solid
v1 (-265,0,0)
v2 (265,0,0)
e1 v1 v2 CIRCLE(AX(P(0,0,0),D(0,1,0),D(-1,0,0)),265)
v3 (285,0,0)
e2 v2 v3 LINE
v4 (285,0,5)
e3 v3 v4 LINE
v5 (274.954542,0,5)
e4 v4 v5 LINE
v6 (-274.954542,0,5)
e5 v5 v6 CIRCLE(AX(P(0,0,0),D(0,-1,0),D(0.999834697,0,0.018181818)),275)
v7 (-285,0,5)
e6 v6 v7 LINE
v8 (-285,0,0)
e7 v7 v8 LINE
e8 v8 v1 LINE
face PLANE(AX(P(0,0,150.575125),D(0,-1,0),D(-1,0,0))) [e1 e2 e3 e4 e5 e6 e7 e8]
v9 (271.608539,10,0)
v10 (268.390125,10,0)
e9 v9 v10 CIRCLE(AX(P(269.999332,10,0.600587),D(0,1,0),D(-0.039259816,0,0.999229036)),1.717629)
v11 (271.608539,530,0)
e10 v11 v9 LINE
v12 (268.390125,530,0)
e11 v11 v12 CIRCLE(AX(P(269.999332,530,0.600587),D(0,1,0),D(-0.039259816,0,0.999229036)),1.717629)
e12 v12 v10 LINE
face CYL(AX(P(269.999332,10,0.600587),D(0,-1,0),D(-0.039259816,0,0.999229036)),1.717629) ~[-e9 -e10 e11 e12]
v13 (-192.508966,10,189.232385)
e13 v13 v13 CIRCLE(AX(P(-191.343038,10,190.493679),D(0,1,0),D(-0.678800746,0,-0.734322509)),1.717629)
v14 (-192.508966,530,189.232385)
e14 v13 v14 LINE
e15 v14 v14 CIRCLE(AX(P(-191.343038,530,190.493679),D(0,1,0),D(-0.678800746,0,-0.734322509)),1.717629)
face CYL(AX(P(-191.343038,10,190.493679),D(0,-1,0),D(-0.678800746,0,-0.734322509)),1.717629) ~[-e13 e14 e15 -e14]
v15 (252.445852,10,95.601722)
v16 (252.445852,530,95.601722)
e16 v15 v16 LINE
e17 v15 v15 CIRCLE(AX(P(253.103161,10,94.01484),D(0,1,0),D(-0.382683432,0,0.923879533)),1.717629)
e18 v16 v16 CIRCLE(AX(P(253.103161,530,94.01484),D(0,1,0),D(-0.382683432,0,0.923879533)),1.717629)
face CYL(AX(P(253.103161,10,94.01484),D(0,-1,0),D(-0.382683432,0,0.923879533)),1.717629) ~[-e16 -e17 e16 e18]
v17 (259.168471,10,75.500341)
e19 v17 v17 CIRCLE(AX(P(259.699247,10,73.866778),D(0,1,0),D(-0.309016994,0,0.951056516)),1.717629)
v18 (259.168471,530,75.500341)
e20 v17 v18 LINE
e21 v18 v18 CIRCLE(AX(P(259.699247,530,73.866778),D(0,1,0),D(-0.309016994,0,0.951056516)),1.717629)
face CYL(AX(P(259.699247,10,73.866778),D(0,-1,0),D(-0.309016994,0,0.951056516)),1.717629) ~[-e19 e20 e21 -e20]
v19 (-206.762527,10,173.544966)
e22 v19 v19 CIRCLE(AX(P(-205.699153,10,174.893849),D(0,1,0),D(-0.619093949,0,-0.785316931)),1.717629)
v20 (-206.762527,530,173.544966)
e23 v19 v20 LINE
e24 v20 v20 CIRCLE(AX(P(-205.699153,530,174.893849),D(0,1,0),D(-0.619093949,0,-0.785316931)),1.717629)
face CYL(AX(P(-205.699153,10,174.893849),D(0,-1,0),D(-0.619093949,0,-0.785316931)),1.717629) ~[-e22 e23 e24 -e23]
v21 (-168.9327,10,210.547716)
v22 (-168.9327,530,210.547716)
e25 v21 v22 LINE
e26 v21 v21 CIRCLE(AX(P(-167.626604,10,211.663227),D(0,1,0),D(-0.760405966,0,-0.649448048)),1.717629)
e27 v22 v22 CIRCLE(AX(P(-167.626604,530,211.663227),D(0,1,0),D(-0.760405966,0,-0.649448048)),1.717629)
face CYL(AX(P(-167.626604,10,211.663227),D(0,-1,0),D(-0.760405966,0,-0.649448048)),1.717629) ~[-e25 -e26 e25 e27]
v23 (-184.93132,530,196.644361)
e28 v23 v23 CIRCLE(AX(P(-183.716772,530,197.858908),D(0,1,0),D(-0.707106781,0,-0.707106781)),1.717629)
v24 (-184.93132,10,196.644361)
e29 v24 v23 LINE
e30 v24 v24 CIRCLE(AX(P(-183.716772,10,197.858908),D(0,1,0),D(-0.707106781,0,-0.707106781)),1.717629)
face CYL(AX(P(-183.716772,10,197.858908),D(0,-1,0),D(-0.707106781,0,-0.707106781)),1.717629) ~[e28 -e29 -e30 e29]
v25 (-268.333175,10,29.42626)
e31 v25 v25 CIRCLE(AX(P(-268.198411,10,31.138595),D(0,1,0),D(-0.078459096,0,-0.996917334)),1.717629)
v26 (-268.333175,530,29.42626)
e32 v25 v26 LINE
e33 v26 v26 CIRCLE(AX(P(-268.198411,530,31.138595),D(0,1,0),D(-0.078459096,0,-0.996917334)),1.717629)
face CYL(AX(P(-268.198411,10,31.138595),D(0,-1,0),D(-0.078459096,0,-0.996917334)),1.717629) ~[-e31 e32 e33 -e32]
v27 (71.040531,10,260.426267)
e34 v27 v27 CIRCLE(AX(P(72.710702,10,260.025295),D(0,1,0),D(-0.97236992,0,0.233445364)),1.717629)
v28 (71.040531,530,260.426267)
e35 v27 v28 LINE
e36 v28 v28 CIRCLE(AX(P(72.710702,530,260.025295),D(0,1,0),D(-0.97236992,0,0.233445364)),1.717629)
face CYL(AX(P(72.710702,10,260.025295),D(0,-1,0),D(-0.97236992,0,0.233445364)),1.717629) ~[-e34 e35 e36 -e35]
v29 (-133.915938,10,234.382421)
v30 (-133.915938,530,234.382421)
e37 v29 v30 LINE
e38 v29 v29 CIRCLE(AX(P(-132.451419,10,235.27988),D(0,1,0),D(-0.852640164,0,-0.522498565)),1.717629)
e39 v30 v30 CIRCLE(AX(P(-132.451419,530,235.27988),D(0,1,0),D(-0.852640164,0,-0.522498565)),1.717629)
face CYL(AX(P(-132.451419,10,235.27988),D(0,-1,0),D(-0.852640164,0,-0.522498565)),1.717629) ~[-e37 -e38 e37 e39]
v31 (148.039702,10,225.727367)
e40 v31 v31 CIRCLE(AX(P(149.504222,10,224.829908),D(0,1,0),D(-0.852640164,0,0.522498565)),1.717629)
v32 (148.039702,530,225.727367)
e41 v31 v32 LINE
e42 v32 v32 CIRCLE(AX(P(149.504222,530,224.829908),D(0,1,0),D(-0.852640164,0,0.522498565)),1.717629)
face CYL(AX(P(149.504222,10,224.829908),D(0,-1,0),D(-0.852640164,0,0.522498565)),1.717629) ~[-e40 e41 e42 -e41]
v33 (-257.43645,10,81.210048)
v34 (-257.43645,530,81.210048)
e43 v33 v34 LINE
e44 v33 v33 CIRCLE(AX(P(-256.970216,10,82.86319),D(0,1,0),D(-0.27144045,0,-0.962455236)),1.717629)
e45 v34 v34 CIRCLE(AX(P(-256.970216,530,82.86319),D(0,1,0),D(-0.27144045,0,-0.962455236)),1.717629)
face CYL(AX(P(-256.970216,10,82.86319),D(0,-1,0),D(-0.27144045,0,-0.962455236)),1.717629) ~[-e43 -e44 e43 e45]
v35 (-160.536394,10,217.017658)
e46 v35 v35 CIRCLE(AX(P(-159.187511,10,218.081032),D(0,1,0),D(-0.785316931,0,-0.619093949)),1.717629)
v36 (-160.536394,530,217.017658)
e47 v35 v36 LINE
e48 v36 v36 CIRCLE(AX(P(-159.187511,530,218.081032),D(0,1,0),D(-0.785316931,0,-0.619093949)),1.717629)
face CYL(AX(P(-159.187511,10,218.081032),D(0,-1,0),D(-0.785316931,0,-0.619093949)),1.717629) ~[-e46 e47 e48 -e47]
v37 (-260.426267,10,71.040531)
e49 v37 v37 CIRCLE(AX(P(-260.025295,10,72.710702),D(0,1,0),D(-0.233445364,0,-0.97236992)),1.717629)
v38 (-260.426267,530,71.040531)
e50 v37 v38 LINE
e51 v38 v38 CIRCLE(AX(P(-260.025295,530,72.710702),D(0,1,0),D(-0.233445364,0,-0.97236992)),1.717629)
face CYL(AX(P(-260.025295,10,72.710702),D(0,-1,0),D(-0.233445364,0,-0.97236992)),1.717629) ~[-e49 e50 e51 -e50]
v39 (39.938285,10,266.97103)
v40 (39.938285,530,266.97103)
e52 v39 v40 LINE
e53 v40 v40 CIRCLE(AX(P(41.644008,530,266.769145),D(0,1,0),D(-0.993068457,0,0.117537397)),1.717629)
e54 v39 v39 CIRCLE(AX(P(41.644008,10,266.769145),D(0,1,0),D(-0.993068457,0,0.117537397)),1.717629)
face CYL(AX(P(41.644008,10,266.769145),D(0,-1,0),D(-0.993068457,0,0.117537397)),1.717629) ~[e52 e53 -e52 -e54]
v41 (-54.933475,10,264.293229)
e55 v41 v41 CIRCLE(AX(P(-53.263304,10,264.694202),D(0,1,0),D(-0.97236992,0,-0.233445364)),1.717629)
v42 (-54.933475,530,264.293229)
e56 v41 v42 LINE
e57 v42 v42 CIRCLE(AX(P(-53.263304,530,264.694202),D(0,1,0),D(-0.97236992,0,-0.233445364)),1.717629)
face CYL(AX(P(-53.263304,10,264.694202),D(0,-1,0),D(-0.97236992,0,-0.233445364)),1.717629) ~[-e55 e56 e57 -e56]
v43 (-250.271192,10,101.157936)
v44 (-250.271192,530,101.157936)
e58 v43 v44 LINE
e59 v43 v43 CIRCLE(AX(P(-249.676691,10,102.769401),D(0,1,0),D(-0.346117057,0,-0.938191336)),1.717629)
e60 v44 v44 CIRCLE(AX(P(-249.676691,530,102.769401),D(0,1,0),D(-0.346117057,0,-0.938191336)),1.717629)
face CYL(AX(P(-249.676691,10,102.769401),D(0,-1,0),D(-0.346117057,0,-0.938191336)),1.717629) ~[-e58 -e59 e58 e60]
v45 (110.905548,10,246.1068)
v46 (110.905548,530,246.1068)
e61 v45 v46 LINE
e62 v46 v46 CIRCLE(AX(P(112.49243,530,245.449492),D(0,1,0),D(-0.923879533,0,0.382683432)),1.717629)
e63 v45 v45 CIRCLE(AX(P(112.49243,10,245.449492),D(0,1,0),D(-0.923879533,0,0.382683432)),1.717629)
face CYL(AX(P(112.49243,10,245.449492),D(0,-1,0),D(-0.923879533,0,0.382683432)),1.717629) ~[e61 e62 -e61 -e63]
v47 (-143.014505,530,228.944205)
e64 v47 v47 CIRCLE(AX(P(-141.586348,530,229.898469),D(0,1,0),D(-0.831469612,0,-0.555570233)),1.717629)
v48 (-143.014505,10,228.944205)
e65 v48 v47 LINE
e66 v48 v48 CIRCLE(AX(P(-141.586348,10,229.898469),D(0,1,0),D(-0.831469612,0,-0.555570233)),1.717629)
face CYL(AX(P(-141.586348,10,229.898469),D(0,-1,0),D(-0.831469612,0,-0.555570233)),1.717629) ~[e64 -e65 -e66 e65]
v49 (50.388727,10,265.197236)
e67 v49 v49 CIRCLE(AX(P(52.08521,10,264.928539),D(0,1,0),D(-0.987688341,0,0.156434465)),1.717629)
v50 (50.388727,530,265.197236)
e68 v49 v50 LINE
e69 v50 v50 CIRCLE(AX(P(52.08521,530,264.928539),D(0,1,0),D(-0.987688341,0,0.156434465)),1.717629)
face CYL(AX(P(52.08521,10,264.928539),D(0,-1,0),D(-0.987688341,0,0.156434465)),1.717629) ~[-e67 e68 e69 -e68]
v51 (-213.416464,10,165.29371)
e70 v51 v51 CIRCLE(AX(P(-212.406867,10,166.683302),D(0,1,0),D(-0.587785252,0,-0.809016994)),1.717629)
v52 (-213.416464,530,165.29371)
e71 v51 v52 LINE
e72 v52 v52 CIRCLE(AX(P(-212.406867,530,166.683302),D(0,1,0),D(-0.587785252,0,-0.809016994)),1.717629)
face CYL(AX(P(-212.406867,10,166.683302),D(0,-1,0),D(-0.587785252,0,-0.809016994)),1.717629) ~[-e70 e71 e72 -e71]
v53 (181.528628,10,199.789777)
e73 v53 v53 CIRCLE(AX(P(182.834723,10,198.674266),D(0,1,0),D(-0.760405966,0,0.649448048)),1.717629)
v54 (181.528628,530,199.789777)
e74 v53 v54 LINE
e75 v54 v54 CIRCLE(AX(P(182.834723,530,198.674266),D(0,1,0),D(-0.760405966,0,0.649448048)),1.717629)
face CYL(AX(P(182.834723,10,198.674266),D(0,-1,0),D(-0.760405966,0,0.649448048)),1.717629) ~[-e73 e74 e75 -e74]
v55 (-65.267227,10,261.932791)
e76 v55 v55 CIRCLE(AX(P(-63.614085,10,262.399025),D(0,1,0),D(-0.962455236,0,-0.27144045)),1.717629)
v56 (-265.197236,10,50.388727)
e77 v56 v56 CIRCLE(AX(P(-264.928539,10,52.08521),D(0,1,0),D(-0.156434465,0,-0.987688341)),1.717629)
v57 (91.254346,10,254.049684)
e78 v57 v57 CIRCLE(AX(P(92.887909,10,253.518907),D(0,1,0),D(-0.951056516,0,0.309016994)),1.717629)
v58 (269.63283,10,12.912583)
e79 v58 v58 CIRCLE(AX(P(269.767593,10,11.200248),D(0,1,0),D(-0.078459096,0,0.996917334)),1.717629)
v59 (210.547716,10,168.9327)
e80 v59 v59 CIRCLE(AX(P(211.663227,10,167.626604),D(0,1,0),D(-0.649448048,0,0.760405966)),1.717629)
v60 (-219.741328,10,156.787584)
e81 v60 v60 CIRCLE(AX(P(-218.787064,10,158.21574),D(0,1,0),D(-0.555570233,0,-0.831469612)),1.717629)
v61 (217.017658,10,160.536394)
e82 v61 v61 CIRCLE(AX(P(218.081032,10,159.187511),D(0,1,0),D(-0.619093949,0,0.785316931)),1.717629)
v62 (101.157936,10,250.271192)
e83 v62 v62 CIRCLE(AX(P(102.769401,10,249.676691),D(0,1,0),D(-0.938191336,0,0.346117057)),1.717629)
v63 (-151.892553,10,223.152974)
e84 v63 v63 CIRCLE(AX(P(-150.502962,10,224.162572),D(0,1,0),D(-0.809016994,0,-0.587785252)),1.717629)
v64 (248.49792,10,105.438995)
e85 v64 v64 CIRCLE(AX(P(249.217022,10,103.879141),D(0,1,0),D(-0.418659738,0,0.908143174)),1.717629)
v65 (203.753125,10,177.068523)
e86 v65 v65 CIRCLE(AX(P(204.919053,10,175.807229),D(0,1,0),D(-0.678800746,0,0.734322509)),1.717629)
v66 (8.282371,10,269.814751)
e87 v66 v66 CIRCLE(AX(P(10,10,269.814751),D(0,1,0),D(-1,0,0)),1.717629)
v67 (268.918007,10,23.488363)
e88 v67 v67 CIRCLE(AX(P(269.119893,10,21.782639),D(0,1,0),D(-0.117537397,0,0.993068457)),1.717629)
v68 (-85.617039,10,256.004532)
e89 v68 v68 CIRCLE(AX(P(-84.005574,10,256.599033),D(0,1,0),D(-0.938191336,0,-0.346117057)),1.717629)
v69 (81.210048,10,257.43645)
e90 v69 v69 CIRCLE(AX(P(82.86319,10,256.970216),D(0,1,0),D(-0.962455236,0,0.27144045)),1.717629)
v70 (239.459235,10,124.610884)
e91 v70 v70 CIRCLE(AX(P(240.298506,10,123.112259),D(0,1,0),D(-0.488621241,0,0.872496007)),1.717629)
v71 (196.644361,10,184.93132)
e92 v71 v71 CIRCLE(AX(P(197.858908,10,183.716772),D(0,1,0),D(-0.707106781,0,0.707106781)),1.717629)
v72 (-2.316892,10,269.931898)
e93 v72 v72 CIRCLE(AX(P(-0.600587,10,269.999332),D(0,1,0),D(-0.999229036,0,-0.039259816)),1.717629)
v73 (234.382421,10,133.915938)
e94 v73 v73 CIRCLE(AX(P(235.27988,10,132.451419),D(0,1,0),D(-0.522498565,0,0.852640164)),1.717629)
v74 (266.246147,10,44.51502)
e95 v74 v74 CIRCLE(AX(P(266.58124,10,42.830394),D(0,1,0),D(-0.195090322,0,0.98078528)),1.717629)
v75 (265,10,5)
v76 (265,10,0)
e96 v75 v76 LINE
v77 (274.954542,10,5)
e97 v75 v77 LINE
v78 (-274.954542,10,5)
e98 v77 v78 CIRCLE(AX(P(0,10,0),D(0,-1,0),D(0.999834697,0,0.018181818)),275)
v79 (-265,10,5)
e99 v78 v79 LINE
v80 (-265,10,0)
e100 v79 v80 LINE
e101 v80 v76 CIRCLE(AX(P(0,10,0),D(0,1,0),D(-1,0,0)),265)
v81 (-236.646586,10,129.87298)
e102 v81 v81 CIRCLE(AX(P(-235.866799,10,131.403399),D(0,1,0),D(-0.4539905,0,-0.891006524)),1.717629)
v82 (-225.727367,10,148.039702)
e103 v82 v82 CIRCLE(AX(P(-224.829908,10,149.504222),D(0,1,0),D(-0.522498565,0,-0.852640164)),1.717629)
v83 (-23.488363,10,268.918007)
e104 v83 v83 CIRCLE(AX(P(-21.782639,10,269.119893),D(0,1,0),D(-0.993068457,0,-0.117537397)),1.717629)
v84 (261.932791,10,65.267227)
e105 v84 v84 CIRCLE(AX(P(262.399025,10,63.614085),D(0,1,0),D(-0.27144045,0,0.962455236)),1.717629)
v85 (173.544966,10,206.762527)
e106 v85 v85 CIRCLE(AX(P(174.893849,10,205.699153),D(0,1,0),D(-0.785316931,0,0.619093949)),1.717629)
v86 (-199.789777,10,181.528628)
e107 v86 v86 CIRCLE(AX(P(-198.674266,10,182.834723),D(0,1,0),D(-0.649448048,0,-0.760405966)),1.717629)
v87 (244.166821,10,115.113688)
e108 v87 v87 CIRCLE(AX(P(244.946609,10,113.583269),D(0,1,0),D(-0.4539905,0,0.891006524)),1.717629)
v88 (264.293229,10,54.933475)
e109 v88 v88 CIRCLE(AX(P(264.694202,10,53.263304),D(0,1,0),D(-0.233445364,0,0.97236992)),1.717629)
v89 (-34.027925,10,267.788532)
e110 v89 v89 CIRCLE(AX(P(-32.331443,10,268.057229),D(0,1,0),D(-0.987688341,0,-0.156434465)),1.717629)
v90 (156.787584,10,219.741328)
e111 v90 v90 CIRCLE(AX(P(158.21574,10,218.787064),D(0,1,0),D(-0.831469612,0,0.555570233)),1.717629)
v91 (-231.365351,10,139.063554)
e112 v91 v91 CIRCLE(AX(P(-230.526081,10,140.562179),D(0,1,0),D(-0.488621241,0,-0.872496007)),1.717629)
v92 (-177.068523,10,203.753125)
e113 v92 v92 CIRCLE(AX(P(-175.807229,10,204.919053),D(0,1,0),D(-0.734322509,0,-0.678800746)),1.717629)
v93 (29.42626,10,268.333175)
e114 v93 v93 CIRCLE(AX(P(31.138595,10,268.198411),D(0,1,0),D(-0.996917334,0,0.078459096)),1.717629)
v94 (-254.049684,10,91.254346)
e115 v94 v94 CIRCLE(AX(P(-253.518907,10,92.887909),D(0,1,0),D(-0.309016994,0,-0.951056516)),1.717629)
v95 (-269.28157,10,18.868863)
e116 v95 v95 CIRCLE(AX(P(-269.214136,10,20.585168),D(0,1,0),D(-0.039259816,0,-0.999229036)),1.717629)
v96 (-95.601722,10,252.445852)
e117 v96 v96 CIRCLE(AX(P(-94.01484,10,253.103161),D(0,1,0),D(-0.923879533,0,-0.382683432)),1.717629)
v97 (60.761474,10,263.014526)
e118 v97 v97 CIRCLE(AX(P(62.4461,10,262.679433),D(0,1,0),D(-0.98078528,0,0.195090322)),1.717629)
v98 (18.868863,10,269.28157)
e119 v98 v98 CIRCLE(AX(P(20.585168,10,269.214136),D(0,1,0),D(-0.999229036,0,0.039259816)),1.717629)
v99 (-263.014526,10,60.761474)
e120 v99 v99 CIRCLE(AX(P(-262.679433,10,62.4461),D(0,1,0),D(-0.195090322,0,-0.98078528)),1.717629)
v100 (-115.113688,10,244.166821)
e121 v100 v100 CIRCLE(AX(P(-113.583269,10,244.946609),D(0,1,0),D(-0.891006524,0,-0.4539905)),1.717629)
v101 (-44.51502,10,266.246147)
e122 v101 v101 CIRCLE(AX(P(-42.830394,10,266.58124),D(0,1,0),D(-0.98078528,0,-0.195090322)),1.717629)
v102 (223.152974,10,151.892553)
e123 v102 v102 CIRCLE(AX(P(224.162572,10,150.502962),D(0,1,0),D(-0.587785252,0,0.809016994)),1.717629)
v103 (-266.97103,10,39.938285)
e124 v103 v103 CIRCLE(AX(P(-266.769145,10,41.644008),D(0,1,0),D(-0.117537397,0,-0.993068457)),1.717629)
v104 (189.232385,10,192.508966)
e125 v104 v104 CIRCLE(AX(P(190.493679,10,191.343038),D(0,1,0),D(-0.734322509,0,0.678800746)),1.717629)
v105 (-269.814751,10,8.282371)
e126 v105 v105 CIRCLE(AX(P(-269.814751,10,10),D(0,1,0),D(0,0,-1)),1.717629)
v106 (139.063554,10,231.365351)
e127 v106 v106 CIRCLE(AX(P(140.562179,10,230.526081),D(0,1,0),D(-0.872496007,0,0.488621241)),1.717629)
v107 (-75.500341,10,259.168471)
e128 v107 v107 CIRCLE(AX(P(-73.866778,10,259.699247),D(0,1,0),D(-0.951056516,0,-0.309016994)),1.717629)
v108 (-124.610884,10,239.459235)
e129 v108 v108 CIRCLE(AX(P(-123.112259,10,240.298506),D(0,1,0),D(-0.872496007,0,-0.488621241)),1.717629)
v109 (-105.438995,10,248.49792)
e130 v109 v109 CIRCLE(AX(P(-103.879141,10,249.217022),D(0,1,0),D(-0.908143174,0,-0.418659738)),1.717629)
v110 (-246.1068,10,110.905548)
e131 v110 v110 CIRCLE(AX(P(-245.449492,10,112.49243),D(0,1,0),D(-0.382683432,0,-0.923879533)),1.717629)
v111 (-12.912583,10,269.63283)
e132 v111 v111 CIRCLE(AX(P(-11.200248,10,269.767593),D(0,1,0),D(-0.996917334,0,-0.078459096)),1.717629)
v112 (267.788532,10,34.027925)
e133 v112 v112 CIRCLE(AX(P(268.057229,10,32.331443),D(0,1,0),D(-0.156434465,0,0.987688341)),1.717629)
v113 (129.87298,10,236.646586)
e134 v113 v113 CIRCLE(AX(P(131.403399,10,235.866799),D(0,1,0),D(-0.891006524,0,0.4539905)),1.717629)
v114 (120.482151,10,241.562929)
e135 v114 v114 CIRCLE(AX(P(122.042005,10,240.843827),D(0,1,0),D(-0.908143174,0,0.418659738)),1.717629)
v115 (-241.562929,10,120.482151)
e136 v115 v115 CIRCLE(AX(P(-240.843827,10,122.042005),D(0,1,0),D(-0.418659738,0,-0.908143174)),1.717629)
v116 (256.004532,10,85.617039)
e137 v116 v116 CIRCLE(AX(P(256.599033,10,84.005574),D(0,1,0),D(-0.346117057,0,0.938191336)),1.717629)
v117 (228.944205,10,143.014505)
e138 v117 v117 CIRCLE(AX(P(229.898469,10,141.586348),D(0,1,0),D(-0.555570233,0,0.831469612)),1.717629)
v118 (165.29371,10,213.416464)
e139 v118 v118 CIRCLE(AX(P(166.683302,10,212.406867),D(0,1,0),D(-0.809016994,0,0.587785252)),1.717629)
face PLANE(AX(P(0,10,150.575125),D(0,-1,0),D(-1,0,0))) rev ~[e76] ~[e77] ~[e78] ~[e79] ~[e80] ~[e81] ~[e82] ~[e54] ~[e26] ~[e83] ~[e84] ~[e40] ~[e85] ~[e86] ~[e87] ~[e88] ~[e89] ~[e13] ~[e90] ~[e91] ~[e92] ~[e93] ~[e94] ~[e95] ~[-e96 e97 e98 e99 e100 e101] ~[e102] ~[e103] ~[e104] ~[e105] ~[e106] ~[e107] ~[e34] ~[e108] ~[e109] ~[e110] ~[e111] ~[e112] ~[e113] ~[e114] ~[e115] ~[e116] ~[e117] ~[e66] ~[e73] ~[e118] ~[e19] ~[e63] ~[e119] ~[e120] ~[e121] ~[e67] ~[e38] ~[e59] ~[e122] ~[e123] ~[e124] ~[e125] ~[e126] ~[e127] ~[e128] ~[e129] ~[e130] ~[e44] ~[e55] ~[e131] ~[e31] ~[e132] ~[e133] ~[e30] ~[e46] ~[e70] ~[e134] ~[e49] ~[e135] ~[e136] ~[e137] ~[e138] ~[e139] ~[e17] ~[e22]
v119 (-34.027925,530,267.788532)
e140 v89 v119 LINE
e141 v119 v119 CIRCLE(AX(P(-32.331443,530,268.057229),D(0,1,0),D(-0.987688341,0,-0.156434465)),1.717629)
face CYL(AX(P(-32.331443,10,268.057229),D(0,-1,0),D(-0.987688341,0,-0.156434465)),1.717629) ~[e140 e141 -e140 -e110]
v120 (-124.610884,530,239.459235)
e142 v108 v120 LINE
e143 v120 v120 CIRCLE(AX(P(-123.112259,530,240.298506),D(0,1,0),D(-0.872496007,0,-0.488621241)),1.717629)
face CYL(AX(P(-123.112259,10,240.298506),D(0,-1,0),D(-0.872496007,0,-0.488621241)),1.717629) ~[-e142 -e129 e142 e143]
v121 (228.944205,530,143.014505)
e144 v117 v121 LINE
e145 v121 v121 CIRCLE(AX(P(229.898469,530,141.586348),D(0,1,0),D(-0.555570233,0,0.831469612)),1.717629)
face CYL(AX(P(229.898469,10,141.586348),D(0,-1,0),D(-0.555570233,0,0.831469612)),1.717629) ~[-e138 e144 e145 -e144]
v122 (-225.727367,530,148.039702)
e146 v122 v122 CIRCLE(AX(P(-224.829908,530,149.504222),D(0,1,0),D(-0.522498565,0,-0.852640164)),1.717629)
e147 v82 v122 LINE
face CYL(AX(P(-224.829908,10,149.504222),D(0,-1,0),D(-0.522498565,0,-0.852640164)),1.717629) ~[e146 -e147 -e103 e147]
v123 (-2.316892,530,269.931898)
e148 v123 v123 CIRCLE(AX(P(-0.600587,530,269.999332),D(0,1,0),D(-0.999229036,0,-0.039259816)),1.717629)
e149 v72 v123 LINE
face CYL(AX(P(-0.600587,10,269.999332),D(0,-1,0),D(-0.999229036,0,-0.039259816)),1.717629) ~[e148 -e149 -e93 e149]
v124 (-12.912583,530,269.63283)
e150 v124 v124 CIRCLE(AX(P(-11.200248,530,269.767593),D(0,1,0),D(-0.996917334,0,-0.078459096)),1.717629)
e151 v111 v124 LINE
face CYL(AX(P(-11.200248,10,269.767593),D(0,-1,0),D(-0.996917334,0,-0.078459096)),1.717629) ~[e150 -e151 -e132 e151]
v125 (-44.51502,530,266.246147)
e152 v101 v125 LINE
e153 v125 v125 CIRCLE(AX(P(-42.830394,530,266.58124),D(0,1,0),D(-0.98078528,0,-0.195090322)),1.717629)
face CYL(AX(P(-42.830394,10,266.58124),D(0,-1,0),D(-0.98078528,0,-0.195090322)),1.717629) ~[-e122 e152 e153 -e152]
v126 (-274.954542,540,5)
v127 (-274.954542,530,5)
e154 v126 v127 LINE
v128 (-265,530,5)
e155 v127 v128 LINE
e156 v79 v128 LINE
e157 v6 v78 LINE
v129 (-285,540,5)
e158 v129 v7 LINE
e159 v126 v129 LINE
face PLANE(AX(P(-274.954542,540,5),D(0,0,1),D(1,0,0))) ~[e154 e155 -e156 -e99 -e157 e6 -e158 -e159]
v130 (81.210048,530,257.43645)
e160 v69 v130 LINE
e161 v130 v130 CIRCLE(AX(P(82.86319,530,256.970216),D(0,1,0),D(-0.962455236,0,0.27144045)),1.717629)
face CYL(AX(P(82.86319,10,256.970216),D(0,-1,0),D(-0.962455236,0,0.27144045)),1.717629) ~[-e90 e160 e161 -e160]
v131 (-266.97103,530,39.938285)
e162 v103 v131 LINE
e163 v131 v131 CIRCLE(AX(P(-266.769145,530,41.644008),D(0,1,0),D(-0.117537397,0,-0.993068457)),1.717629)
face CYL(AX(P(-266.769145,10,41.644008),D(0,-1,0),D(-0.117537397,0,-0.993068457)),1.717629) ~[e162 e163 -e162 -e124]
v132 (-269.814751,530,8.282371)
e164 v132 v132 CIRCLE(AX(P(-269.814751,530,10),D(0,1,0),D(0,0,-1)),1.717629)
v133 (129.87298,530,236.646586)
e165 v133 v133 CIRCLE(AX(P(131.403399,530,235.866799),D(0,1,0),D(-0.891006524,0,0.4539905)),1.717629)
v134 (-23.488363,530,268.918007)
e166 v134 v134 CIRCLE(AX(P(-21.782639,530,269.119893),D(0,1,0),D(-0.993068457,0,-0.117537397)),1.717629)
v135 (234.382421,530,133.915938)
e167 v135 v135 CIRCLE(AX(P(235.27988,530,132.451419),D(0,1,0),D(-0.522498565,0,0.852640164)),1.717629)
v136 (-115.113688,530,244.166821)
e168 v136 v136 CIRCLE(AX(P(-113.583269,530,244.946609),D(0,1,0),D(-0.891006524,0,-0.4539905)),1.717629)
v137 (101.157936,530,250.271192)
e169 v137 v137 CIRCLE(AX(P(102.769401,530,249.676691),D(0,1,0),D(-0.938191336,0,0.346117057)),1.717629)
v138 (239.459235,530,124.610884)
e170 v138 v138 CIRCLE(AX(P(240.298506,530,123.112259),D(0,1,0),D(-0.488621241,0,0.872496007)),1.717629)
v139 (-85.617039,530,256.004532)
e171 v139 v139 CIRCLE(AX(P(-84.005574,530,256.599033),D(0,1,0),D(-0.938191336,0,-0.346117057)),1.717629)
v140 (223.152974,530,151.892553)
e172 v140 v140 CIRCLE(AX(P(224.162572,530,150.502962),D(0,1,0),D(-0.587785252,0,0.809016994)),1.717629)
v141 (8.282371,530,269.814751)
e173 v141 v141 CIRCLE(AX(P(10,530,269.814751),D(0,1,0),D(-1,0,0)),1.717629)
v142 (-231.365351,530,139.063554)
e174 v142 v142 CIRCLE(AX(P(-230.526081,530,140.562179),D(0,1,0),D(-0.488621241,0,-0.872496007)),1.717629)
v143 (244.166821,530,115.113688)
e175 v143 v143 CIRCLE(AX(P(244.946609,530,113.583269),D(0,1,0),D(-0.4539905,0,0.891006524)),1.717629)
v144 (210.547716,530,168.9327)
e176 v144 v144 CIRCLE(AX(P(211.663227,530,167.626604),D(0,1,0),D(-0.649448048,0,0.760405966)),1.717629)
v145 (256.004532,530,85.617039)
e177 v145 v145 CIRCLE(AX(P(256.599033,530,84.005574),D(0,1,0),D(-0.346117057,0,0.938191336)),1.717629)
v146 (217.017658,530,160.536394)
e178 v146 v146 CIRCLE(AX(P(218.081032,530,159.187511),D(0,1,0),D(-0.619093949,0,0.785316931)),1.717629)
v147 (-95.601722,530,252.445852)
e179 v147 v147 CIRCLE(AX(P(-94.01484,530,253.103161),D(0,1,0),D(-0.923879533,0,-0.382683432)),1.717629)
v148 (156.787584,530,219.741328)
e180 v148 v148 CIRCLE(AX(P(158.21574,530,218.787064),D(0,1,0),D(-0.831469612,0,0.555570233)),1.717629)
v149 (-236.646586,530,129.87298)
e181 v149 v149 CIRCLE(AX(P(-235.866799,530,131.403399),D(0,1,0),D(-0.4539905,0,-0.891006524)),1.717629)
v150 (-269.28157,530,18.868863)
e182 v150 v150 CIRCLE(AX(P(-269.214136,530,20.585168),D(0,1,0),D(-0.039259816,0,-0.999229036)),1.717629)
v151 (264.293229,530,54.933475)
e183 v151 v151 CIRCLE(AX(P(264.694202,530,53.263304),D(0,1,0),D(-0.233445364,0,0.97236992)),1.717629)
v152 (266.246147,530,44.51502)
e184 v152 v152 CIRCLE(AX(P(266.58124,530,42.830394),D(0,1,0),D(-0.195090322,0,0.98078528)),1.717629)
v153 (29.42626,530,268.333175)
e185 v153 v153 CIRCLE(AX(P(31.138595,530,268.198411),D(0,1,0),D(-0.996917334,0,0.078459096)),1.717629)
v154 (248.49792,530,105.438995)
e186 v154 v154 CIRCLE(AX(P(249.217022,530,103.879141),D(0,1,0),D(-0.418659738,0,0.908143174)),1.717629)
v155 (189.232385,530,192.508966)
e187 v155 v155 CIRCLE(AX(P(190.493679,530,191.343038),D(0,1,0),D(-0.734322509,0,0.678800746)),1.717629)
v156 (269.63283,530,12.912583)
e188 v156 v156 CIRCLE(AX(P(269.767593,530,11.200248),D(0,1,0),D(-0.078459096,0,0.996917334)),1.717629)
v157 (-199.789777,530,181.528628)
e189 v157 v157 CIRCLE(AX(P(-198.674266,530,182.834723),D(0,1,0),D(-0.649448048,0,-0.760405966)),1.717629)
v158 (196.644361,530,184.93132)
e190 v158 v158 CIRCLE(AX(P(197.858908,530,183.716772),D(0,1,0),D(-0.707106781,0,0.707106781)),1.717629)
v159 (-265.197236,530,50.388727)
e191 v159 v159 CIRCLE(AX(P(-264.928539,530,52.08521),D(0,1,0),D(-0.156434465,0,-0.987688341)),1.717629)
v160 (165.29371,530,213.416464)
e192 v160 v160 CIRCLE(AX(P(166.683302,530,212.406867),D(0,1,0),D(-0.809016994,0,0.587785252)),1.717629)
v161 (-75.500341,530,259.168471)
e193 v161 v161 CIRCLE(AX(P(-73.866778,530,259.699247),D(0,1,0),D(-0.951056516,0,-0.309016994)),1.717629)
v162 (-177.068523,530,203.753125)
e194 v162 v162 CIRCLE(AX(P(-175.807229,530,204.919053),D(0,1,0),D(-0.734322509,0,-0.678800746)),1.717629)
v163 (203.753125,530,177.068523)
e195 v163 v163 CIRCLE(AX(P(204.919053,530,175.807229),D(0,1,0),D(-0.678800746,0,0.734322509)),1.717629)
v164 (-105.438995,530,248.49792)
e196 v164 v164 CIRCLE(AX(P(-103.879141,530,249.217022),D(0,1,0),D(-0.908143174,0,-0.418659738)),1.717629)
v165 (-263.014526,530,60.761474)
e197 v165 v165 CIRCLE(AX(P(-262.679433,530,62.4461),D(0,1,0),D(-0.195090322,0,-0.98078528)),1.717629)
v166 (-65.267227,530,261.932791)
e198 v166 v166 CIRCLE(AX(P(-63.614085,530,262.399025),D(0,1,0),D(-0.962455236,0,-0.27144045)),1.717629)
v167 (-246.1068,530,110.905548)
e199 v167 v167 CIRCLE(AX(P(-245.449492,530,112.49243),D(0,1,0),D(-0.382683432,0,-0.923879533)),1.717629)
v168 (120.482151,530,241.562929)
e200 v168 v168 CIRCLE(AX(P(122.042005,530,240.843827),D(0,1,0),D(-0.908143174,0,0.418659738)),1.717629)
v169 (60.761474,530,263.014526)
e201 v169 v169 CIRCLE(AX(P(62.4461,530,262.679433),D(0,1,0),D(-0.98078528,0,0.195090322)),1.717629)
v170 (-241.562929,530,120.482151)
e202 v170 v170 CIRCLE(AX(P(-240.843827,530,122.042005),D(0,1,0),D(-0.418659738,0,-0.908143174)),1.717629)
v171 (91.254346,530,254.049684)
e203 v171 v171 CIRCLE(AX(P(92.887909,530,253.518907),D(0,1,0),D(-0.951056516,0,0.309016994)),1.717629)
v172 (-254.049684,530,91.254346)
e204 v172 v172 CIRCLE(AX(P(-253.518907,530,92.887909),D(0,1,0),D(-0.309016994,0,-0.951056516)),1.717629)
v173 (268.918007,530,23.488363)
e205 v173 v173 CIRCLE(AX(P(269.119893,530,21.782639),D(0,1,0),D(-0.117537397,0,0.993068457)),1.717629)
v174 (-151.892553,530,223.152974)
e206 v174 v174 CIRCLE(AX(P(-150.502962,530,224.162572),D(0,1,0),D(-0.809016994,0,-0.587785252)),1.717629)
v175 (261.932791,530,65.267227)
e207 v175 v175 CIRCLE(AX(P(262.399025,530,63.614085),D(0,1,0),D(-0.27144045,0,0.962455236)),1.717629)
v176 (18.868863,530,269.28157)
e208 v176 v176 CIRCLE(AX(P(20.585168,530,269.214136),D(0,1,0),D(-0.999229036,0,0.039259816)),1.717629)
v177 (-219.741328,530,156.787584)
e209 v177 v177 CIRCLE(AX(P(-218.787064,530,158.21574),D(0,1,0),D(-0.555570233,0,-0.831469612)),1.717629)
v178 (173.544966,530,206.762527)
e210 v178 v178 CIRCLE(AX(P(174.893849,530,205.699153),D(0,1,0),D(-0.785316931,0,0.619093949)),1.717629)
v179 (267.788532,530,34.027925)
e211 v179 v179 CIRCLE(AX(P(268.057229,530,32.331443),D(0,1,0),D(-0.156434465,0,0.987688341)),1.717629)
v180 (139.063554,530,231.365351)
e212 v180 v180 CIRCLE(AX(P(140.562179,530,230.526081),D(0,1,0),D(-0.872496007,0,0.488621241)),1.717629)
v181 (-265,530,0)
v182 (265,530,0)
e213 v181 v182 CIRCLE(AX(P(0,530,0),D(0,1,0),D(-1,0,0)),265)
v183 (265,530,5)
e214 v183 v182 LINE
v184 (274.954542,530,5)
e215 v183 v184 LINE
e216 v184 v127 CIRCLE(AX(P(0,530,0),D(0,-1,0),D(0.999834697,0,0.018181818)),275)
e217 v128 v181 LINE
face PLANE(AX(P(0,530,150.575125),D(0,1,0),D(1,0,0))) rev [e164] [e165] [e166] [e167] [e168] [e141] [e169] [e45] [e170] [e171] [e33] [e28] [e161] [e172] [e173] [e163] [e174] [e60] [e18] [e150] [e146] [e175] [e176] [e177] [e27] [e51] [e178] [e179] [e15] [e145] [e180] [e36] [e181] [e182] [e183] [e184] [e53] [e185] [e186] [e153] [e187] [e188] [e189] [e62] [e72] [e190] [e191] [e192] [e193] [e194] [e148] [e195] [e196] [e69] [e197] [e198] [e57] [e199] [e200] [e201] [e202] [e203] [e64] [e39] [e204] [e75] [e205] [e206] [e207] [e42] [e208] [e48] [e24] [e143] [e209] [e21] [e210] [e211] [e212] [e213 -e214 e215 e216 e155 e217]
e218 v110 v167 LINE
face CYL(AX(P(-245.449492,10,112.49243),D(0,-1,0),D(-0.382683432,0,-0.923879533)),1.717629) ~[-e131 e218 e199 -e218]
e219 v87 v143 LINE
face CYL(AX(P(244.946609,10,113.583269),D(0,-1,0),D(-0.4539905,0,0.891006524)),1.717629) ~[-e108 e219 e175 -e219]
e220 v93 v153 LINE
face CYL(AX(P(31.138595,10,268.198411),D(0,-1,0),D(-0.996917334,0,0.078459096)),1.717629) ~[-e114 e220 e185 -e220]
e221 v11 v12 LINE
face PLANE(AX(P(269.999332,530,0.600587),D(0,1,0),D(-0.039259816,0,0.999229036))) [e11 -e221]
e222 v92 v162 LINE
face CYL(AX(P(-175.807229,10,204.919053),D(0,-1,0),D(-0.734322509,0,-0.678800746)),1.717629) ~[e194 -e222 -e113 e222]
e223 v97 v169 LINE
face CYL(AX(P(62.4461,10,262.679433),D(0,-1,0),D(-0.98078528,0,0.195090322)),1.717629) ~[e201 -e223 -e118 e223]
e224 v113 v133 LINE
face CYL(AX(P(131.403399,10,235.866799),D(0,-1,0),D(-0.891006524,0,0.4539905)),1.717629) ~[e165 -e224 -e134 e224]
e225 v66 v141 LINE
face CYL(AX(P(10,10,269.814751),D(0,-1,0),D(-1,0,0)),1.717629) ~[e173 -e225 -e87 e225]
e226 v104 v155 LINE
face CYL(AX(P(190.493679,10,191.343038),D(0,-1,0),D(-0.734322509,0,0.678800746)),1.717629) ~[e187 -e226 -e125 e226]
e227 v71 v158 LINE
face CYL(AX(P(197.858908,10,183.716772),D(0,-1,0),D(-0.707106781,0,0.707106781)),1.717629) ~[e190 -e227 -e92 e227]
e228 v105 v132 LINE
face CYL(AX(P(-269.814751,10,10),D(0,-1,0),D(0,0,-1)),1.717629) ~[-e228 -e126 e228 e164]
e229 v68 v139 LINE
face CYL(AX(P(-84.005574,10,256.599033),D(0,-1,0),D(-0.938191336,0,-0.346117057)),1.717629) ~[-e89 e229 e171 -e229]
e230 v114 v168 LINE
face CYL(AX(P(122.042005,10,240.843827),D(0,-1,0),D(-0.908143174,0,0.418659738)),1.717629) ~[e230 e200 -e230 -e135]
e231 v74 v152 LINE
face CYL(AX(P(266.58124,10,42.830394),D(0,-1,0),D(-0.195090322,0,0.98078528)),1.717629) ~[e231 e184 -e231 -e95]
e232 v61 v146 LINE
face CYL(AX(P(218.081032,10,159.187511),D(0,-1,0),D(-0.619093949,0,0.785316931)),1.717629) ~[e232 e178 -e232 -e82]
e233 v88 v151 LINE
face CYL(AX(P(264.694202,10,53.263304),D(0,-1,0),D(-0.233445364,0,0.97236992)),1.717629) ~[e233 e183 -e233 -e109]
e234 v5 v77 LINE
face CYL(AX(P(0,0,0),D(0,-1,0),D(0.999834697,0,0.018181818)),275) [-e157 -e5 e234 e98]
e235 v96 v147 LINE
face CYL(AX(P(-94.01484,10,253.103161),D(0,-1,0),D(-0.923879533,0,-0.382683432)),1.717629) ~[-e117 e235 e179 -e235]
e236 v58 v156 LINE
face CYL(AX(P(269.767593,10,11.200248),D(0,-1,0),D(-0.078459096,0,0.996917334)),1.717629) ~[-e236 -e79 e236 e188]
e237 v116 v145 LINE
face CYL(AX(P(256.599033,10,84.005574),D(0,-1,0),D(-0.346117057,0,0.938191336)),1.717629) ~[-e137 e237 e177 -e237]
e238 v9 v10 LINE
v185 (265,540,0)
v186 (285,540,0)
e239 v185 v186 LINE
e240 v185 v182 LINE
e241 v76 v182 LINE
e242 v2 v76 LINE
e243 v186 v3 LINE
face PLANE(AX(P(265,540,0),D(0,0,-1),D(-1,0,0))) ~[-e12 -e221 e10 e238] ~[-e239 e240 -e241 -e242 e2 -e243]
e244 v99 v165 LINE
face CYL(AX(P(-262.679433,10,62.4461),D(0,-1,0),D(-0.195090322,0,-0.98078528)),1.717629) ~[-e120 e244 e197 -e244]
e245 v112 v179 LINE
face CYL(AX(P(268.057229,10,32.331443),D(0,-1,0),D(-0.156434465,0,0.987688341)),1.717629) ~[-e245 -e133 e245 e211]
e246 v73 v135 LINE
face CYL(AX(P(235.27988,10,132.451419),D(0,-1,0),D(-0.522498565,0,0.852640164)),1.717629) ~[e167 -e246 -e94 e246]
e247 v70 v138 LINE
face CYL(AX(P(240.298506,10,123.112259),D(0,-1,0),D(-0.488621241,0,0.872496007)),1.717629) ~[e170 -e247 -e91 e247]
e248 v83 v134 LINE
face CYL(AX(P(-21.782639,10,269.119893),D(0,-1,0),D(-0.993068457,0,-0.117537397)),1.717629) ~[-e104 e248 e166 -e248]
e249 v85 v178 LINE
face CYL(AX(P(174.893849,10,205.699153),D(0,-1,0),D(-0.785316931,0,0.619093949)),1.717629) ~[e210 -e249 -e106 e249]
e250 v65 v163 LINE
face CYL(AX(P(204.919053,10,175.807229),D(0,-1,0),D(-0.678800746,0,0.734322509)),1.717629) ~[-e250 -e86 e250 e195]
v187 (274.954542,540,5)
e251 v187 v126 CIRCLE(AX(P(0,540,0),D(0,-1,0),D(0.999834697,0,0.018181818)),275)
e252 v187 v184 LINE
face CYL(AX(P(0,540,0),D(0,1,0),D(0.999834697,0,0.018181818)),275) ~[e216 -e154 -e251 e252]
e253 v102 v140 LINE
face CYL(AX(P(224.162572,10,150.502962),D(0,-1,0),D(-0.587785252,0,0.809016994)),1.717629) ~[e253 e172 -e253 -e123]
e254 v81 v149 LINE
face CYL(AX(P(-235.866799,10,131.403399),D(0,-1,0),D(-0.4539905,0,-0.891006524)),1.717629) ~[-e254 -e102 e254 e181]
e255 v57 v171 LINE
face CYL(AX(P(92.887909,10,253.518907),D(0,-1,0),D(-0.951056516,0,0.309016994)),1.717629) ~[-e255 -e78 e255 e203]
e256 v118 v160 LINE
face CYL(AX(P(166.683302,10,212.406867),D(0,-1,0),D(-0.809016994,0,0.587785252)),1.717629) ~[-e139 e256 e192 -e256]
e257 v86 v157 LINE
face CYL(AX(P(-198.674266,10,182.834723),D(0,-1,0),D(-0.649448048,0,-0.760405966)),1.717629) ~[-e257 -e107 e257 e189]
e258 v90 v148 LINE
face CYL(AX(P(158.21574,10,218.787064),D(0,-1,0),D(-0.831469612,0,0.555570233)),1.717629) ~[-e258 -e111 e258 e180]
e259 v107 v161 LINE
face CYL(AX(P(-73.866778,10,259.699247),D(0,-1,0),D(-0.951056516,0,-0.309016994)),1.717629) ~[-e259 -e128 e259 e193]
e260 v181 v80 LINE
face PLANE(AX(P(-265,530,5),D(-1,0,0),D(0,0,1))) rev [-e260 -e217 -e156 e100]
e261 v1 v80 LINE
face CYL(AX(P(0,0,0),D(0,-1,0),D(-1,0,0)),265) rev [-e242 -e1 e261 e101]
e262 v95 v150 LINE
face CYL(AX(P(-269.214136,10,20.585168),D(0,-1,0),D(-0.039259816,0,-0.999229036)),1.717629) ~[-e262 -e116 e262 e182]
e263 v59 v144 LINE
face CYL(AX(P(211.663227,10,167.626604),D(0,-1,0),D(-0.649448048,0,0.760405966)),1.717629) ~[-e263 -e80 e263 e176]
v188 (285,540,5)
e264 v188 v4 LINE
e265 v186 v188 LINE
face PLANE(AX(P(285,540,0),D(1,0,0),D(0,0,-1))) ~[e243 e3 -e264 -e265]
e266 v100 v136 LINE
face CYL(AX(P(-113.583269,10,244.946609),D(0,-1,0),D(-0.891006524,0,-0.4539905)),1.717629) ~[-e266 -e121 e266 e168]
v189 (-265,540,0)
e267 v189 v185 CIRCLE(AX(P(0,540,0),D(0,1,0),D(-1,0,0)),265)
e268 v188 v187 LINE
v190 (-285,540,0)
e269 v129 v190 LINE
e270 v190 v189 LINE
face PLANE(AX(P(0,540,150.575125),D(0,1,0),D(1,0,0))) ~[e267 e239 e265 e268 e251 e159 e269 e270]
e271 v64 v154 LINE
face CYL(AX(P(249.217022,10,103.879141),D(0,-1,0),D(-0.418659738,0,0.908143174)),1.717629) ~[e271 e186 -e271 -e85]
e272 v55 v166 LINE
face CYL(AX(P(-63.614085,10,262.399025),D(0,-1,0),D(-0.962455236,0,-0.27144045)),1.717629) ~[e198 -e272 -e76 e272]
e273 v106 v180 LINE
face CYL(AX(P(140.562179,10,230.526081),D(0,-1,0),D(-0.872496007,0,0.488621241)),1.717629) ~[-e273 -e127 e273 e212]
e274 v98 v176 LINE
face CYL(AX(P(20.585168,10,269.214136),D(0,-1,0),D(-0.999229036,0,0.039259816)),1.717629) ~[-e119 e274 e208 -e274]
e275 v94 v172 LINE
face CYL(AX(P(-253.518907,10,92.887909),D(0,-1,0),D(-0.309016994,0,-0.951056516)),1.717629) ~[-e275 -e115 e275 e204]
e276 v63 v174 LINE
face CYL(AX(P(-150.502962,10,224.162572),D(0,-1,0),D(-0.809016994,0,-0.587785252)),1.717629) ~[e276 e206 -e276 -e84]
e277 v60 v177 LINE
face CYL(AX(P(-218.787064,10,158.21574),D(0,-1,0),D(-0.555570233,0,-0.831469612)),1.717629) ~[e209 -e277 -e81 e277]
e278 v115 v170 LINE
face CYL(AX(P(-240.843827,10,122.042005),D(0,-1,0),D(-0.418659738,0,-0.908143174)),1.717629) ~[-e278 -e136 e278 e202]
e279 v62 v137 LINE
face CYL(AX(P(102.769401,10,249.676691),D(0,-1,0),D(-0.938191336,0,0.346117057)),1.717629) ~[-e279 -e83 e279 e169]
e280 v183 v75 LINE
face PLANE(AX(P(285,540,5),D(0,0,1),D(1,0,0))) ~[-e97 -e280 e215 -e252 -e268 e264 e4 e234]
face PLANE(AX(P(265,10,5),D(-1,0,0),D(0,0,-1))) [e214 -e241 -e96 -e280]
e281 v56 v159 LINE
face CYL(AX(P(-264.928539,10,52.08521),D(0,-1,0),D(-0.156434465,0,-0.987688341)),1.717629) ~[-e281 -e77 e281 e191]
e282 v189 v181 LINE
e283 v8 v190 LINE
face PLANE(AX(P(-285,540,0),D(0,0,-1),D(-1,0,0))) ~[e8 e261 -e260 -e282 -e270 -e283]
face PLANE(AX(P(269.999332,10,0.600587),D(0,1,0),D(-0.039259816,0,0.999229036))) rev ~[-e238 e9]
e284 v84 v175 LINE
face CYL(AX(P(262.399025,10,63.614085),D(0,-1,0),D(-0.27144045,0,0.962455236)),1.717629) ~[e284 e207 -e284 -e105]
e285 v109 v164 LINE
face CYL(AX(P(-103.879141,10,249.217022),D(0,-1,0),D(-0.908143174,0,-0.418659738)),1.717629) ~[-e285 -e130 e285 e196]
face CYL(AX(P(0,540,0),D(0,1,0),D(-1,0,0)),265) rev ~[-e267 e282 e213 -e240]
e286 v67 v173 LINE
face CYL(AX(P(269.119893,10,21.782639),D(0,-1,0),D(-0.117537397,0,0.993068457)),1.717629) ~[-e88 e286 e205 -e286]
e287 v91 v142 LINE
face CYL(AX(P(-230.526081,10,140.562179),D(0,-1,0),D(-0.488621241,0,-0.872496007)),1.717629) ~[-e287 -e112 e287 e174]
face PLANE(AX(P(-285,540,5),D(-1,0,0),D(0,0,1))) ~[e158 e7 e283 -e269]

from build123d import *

# Parameters (mm, degrees)
BOSS_EXTRUDE1_DEPTH = 10
SKETCH2_W           = 20
SKETCH2_H           = 5
BOSS_EXTRUDE2_DEPTH = 260
SKETCH3_R           = 1.717629463
BOSS_EXTRUDE3_DEPTH = 520
CIRPATTERN1_COUNT   = 80
CIRPATTERN1_ANGLE   = 177.75


with BuildPart() as part:
    # Sketch1 → Boss-Extrude1 (new body)
    with BuildSketch(Plane(origin=(0, 0, 0), x_dir=(1, 0, 0), z_dir=(0, 1, 0))):
        with BuildLine():
            Line((265, 0), (275, 0))
            Line((275, 0), (285, 0))
            Line((285, 0), (285, -5))
            Line((285, -5), (274.954541697, -5))
            ThreePointArc((274.954541697, -5), (0, -275), (-274.954541697, -5))
            Line((-274.954541697, -5), (-285, -5))
            Line((-285, -5), (-285, 0))
            Line((-285, 0), (-275, 0))
            Line((-275, 0), (-265, 0))
            ThreePointArc((-265, 0), (0, -265), (265, 0))
        make_face()
    boss_extrude1 = extrude(amount=BOSS_EXTRUDE1_DEPTH)

    # Sketch2 → Boss-Extrude2 (add)
    with BuildSketch(Plane(origin=(0, 10, 0), x_dir=(1, 0, 0), z_dir=(0, 1, 0))):
        with Locations((-275, -2.5)):
            Rectangle(SKETCH2_W, SKETCH2_H)
        with Locations((275, -2.5)):
            Rectangle(SKETCH2_W, SKETCH2_H)
    boss_extrude2 = extrude(amount=BOSS_EXTRUDE2_DEPTH)

    # Mirror2: Boss-Extrude2 across plane
    add(boss_extrude2.mirror(Plane.ZX.offset(270)))

    # Mirror3: Boss-Extrude1 across plane
    add(boss_extrude1.mirror(Plane.ZX.offset(270)))

    # Sketch3 → Boss-Extrude3 (add)
    with BuildSketch(Plane(origin=(0, 10, 0), x_dir=(1, 0, 0), z_dir=(0, 1, 0))):
        with Locations(Location((-269.814751265, -10, 0), (0, 0, 90))):
            Circle(SKETCH3_R)
    boss_extrude3 = extrude(amount=BOSS_EXTRUDE3_DEPTH)

    # CirPattern1: Boss-Extrude3 ×80 about axis
    cirpattern1_axis = Axis((0, 0, 0), (0, 1, 0))
    for i in range(1, CIRPATTERN1_COUNT):
        add(boss_extrude3.rotate(cirpattern1_axis, i * CIRPATTERN1_ANGLE / (CIRPATTERN1_COUNT - 1)))


solid = part.part
